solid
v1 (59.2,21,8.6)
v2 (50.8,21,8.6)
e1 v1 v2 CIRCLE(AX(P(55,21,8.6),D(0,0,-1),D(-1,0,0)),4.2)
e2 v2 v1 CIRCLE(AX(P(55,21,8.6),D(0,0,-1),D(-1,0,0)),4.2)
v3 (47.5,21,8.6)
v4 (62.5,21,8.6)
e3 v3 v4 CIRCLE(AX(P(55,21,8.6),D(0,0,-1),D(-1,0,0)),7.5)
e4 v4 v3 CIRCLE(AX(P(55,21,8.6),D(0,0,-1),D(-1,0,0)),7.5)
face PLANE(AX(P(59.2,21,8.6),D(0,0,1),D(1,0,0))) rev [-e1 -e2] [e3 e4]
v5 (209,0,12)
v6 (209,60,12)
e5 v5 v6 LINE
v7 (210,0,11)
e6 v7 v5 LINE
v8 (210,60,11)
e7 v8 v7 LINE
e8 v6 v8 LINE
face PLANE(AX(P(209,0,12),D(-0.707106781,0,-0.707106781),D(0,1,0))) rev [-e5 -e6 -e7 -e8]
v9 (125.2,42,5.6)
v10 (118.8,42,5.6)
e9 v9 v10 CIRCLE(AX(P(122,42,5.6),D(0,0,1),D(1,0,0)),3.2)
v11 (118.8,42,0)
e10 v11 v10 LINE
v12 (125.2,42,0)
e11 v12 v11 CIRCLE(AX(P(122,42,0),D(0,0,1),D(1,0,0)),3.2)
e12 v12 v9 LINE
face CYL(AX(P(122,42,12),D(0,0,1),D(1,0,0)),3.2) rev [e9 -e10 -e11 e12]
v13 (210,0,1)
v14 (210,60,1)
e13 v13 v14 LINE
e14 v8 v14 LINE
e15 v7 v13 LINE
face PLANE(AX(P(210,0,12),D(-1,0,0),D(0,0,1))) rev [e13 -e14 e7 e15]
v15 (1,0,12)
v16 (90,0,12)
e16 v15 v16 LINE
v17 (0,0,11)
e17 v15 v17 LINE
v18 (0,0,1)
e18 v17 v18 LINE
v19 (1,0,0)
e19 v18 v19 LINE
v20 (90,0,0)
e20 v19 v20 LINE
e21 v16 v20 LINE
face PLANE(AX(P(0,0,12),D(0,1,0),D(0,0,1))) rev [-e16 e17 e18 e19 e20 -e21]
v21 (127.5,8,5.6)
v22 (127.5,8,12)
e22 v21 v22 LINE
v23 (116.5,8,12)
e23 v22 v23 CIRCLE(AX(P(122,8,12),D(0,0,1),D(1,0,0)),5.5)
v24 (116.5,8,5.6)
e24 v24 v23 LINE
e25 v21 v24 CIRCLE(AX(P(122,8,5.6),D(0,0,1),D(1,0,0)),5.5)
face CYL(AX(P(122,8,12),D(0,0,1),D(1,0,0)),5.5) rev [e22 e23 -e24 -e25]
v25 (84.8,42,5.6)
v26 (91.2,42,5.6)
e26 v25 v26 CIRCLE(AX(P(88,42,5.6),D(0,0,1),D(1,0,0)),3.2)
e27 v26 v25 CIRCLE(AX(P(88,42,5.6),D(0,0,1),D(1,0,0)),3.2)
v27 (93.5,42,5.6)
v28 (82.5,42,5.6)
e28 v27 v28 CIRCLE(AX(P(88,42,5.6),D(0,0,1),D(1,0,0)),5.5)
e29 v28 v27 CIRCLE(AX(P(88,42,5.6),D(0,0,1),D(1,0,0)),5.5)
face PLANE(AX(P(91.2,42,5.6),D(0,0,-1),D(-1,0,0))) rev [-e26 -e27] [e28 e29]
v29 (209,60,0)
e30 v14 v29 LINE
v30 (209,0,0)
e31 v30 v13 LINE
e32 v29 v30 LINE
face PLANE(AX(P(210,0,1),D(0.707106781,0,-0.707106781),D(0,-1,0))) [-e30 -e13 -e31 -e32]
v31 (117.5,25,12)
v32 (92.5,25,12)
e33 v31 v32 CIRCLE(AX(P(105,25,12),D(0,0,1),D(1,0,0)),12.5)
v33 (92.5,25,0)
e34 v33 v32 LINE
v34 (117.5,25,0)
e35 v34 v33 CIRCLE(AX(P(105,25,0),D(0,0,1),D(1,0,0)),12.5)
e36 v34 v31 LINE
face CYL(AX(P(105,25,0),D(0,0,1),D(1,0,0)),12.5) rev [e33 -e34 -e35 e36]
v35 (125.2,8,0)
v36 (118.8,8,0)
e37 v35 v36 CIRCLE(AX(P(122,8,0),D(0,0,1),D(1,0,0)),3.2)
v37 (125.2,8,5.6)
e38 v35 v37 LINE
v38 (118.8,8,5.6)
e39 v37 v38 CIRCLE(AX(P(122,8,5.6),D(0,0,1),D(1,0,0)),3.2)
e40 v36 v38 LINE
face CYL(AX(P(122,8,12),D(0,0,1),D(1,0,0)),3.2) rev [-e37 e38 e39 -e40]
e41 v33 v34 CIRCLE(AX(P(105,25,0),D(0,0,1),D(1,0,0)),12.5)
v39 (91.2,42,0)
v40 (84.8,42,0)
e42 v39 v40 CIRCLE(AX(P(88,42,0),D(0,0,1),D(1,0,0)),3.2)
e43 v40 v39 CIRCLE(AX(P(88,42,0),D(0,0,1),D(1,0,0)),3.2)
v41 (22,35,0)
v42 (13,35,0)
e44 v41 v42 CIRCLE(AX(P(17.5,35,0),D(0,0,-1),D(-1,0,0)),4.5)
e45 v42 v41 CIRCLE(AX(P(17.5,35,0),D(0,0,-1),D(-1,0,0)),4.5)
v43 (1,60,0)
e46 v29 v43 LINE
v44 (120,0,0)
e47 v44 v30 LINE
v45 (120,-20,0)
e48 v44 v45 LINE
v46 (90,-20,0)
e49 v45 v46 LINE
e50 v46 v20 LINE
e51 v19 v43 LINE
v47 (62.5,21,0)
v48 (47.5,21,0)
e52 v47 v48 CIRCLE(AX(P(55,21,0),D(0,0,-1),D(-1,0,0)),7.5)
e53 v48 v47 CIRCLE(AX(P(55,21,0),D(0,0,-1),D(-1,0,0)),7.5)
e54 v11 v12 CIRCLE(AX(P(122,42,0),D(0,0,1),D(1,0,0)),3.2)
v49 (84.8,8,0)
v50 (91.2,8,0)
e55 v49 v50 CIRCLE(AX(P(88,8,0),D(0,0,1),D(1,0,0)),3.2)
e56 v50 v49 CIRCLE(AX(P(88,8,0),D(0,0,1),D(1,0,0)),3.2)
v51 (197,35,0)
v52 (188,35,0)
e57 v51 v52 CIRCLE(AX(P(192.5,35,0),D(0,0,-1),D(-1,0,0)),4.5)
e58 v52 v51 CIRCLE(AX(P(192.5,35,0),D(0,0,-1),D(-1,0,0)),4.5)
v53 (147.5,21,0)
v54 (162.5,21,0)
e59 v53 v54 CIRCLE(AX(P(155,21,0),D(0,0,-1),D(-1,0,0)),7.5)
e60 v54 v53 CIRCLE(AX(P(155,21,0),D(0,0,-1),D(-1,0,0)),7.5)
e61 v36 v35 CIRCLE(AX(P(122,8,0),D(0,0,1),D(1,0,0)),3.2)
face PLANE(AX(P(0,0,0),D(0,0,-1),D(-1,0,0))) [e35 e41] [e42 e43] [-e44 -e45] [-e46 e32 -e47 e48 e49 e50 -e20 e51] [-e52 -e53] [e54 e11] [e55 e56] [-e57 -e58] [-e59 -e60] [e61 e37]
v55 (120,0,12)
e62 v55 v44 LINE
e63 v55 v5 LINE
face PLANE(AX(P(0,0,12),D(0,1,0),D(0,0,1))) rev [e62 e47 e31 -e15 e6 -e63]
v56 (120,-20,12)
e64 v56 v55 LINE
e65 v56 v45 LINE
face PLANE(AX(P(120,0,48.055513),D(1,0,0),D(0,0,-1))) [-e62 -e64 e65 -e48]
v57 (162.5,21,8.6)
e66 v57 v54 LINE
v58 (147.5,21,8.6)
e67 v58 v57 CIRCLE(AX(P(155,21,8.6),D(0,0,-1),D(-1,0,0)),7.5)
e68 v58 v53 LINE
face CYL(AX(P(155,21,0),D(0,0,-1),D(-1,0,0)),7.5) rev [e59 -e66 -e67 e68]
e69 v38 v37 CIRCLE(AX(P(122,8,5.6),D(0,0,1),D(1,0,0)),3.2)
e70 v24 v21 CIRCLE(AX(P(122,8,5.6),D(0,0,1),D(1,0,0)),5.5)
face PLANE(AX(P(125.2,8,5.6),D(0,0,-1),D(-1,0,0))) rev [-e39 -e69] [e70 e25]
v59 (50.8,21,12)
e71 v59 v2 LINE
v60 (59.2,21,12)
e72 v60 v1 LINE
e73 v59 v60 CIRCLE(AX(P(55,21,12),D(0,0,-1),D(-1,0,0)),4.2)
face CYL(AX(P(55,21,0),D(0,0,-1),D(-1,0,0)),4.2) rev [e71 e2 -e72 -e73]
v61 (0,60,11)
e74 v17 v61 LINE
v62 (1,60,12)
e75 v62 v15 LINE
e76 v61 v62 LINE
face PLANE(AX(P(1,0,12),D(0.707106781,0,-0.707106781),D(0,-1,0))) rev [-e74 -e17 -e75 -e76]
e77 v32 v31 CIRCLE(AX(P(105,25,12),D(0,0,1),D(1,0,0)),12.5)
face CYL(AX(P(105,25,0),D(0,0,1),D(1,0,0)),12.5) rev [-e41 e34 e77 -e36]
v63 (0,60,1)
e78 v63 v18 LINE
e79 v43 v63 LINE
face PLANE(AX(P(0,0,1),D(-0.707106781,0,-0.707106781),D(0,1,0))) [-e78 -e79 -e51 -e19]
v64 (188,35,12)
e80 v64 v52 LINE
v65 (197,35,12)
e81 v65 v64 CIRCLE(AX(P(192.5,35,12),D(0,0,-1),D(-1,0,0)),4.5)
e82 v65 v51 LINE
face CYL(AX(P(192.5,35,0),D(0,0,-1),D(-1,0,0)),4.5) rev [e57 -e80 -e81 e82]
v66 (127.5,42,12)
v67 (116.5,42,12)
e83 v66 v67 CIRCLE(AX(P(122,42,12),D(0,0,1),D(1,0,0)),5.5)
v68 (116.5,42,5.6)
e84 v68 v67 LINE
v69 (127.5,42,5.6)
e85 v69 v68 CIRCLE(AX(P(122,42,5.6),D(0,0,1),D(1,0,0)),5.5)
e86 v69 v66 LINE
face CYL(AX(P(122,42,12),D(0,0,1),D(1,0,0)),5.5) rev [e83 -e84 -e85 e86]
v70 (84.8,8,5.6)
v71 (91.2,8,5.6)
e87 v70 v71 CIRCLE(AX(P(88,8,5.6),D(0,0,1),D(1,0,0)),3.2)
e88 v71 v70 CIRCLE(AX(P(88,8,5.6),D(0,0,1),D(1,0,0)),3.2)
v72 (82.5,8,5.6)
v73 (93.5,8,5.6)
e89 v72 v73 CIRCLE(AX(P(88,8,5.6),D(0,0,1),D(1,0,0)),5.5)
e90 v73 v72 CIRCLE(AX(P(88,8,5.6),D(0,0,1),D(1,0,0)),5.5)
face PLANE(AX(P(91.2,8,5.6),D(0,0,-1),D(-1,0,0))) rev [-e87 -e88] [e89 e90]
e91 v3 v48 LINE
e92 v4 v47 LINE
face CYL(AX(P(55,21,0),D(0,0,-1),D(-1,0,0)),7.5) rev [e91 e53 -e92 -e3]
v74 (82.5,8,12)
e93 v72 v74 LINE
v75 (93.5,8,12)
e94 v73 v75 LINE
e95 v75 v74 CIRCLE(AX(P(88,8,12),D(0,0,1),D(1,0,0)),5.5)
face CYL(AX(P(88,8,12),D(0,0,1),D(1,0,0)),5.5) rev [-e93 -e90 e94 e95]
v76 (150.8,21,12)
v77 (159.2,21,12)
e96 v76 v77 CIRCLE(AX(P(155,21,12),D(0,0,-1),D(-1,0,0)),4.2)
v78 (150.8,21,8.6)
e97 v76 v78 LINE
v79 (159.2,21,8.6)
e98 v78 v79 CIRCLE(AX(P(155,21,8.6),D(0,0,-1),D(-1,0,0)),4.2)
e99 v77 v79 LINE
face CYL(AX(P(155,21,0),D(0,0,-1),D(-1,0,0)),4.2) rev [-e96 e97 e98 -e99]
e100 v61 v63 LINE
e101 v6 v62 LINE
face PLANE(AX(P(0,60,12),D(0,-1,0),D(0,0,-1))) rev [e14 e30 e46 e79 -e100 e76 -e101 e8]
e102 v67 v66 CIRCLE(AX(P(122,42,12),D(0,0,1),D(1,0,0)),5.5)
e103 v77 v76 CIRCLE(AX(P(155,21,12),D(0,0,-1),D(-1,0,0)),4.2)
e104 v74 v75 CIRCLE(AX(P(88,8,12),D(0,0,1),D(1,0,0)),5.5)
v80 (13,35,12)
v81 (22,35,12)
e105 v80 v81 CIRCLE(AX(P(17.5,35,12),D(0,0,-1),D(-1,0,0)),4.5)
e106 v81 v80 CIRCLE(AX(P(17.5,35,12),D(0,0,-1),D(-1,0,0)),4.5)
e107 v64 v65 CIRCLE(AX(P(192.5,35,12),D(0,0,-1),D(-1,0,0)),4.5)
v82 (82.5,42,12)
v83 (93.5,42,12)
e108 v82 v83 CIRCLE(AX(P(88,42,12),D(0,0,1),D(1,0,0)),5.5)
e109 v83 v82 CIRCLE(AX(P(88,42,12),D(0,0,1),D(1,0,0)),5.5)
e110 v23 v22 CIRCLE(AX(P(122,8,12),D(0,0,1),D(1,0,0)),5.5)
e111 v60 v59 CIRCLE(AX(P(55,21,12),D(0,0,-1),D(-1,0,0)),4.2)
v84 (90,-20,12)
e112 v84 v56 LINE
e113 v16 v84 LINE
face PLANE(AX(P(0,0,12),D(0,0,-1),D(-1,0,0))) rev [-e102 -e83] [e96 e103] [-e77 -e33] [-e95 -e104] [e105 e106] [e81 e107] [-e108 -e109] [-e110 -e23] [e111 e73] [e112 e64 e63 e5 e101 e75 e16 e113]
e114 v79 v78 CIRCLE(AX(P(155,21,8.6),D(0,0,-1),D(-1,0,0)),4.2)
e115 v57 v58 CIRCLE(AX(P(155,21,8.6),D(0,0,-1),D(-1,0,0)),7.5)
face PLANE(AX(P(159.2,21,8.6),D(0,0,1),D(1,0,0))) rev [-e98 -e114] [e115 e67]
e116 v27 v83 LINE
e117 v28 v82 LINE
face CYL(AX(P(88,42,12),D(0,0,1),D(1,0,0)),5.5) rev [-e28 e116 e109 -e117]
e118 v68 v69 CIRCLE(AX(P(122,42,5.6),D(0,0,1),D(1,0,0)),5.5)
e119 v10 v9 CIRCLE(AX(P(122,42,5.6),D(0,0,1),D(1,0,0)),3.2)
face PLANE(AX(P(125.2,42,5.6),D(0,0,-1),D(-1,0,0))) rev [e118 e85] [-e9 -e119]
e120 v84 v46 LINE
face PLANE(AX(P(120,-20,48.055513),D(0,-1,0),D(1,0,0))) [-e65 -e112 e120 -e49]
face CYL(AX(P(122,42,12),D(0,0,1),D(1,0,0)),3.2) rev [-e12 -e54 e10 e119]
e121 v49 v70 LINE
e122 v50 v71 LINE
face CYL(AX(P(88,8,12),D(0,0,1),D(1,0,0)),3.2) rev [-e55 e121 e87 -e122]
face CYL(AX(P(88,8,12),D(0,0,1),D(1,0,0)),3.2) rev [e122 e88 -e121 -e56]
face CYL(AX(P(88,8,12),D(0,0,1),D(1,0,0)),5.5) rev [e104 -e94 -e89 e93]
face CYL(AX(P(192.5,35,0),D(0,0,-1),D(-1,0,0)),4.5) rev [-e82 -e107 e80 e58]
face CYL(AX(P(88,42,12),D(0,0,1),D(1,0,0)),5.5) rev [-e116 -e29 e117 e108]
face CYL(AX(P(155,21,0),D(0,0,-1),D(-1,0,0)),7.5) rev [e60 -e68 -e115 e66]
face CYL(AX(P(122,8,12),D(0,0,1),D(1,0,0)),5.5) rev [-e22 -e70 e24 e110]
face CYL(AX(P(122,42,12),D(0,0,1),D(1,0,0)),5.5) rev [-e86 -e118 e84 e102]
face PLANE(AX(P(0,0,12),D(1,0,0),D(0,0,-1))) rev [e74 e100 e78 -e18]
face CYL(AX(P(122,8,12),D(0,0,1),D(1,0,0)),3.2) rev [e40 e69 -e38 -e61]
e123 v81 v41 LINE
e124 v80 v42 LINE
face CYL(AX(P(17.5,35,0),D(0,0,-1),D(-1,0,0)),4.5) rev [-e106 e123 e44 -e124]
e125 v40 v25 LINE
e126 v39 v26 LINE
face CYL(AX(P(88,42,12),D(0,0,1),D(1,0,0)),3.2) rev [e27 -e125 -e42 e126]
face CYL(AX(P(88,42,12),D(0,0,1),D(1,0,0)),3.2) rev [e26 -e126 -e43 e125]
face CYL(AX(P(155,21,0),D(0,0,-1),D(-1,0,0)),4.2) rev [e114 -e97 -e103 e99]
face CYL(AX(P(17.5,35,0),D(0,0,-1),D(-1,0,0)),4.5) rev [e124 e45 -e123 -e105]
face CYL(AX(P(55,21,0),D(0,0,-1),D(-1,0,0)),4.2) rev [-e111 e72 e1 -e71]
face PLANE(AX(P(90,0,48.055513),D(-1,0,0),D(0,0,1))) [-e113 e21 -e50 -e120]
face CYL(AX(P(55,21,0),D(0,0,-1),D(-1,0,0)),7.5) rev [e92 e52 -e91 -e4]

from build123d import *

# Parameters (mm, degrees)
SKETCH_1_W                   = 210
SKETCH_1_H                   = 60
EXTRUDE_1_DEPTH              = 12
SKETCH_2_R                   = 12.5
CUT_EXTRUDE_1_DEPTH          = 12
HOLE_WIZARD_M8_1_D           = 8.4
HOLE_WIZARD_M8_1_CBORE_D     = 15
HOLE_WIZARD_M8_1_CBORE_DEPTH = 8.6
HOLE_WIZARD_M6_2_D           = 6.4
HOLE_WIZARD_M6_2_CBORE_D     = 11
HOLE_WIZARD_M6_2_CBORE_DEPTH = 6.4
CHAMFER_1_SIZE               = 1
HOLE_WIZARD_9_0_9_1_D        = 9
SKETCH_14_W                  = 30
SKETCH_14_H                  = 20
EXTRUDE_2_DEPTH              = 12


with BuildPart() as part:
    # 草图1 → 凸台-拉伸1 (new body)
    with BuildSketch(Plane.XY):
        with Locations((105, 30)):
            Rectangle(SKETCH_1_W, SKETCH_1_H)
    extrude(amount=EXTRUDE_1_DEPTH)

    # 草图2 → 切除-拉伸1 (cut)
    with BuildSketch(Plane.XY.offset(12)):
        with Locations((105, 25)):
            Circle(SKETCH_2_R)
    extrude(amount=-CUT_EXTRUDE_1_DEPTH, mode=Mode.SUBTRACT)

    # M8 六角凹头螺钉的柱形沉头孔1 (through all)
    with Locations(Plane(origin=(0, 0, 0), x_dir=(-1, 0, 0), z_dir=(0, 0, -1))):
        with Locations((-55, 21), (-155, 21)):
            CounterBoreHole(HOLE_WIZARD_M8_1_D / 2, HOLE_WIZARD_M8_1_CBORE_D / 2, HOLE_WIZARD_M8_1_CBORE_DEPTH)

    # M6 六角凹头螺钉的柱形沉头孔2 (through all)
    with Locations(Plane.XY.offset(12)):
        with Locations((122, 42), (88, 42), (122, 8), (88, 8)):
            CounterBoreHole(HOLE_WIZARD_M6_2_D / 2, HOLE_WIZARD_M6_2_CBORE_D / 2, HOLE_WIZARD_M6_2_CBORE_DEPTH)

    # 倒角1
    chamfer_1_edges = [part.edges().sort_by_distance(p)[0] for p in [
        (210, 30, 12),
        (0, 30, 12),
        (210, 30, 0),
        (0, 30, 0),
    ]]
    chamfer(chamfer_1_edges, length=CHAMFER_1_SIZE)

    # Ø9.0 (9) 直径孔1 (through all)
    with Locations(Plane(origin=(0, 0, 0), x_dir=(-1, 0, 0), z_dir=(0, 0, -1))):
        with Locations((-192.5, 35), (-17.5, 35)):
            Hole(HOLE_WIZARD_9_0_9_1_D / 2)

    # 草图14 → 凸台-拉伸2 (add)
    with BuildSketch(Plane(origin=(0, 0, 0), x_dir=(-1, 0, 0), z_dir=(0, 0, -1))):
        with Locations((-105, -10)):
            Rectangle(SKETCH_14_W, SKETCH_14_H)
    extrude(amount=-EXTRUDE_2_DEPTH)


solid = part.part
